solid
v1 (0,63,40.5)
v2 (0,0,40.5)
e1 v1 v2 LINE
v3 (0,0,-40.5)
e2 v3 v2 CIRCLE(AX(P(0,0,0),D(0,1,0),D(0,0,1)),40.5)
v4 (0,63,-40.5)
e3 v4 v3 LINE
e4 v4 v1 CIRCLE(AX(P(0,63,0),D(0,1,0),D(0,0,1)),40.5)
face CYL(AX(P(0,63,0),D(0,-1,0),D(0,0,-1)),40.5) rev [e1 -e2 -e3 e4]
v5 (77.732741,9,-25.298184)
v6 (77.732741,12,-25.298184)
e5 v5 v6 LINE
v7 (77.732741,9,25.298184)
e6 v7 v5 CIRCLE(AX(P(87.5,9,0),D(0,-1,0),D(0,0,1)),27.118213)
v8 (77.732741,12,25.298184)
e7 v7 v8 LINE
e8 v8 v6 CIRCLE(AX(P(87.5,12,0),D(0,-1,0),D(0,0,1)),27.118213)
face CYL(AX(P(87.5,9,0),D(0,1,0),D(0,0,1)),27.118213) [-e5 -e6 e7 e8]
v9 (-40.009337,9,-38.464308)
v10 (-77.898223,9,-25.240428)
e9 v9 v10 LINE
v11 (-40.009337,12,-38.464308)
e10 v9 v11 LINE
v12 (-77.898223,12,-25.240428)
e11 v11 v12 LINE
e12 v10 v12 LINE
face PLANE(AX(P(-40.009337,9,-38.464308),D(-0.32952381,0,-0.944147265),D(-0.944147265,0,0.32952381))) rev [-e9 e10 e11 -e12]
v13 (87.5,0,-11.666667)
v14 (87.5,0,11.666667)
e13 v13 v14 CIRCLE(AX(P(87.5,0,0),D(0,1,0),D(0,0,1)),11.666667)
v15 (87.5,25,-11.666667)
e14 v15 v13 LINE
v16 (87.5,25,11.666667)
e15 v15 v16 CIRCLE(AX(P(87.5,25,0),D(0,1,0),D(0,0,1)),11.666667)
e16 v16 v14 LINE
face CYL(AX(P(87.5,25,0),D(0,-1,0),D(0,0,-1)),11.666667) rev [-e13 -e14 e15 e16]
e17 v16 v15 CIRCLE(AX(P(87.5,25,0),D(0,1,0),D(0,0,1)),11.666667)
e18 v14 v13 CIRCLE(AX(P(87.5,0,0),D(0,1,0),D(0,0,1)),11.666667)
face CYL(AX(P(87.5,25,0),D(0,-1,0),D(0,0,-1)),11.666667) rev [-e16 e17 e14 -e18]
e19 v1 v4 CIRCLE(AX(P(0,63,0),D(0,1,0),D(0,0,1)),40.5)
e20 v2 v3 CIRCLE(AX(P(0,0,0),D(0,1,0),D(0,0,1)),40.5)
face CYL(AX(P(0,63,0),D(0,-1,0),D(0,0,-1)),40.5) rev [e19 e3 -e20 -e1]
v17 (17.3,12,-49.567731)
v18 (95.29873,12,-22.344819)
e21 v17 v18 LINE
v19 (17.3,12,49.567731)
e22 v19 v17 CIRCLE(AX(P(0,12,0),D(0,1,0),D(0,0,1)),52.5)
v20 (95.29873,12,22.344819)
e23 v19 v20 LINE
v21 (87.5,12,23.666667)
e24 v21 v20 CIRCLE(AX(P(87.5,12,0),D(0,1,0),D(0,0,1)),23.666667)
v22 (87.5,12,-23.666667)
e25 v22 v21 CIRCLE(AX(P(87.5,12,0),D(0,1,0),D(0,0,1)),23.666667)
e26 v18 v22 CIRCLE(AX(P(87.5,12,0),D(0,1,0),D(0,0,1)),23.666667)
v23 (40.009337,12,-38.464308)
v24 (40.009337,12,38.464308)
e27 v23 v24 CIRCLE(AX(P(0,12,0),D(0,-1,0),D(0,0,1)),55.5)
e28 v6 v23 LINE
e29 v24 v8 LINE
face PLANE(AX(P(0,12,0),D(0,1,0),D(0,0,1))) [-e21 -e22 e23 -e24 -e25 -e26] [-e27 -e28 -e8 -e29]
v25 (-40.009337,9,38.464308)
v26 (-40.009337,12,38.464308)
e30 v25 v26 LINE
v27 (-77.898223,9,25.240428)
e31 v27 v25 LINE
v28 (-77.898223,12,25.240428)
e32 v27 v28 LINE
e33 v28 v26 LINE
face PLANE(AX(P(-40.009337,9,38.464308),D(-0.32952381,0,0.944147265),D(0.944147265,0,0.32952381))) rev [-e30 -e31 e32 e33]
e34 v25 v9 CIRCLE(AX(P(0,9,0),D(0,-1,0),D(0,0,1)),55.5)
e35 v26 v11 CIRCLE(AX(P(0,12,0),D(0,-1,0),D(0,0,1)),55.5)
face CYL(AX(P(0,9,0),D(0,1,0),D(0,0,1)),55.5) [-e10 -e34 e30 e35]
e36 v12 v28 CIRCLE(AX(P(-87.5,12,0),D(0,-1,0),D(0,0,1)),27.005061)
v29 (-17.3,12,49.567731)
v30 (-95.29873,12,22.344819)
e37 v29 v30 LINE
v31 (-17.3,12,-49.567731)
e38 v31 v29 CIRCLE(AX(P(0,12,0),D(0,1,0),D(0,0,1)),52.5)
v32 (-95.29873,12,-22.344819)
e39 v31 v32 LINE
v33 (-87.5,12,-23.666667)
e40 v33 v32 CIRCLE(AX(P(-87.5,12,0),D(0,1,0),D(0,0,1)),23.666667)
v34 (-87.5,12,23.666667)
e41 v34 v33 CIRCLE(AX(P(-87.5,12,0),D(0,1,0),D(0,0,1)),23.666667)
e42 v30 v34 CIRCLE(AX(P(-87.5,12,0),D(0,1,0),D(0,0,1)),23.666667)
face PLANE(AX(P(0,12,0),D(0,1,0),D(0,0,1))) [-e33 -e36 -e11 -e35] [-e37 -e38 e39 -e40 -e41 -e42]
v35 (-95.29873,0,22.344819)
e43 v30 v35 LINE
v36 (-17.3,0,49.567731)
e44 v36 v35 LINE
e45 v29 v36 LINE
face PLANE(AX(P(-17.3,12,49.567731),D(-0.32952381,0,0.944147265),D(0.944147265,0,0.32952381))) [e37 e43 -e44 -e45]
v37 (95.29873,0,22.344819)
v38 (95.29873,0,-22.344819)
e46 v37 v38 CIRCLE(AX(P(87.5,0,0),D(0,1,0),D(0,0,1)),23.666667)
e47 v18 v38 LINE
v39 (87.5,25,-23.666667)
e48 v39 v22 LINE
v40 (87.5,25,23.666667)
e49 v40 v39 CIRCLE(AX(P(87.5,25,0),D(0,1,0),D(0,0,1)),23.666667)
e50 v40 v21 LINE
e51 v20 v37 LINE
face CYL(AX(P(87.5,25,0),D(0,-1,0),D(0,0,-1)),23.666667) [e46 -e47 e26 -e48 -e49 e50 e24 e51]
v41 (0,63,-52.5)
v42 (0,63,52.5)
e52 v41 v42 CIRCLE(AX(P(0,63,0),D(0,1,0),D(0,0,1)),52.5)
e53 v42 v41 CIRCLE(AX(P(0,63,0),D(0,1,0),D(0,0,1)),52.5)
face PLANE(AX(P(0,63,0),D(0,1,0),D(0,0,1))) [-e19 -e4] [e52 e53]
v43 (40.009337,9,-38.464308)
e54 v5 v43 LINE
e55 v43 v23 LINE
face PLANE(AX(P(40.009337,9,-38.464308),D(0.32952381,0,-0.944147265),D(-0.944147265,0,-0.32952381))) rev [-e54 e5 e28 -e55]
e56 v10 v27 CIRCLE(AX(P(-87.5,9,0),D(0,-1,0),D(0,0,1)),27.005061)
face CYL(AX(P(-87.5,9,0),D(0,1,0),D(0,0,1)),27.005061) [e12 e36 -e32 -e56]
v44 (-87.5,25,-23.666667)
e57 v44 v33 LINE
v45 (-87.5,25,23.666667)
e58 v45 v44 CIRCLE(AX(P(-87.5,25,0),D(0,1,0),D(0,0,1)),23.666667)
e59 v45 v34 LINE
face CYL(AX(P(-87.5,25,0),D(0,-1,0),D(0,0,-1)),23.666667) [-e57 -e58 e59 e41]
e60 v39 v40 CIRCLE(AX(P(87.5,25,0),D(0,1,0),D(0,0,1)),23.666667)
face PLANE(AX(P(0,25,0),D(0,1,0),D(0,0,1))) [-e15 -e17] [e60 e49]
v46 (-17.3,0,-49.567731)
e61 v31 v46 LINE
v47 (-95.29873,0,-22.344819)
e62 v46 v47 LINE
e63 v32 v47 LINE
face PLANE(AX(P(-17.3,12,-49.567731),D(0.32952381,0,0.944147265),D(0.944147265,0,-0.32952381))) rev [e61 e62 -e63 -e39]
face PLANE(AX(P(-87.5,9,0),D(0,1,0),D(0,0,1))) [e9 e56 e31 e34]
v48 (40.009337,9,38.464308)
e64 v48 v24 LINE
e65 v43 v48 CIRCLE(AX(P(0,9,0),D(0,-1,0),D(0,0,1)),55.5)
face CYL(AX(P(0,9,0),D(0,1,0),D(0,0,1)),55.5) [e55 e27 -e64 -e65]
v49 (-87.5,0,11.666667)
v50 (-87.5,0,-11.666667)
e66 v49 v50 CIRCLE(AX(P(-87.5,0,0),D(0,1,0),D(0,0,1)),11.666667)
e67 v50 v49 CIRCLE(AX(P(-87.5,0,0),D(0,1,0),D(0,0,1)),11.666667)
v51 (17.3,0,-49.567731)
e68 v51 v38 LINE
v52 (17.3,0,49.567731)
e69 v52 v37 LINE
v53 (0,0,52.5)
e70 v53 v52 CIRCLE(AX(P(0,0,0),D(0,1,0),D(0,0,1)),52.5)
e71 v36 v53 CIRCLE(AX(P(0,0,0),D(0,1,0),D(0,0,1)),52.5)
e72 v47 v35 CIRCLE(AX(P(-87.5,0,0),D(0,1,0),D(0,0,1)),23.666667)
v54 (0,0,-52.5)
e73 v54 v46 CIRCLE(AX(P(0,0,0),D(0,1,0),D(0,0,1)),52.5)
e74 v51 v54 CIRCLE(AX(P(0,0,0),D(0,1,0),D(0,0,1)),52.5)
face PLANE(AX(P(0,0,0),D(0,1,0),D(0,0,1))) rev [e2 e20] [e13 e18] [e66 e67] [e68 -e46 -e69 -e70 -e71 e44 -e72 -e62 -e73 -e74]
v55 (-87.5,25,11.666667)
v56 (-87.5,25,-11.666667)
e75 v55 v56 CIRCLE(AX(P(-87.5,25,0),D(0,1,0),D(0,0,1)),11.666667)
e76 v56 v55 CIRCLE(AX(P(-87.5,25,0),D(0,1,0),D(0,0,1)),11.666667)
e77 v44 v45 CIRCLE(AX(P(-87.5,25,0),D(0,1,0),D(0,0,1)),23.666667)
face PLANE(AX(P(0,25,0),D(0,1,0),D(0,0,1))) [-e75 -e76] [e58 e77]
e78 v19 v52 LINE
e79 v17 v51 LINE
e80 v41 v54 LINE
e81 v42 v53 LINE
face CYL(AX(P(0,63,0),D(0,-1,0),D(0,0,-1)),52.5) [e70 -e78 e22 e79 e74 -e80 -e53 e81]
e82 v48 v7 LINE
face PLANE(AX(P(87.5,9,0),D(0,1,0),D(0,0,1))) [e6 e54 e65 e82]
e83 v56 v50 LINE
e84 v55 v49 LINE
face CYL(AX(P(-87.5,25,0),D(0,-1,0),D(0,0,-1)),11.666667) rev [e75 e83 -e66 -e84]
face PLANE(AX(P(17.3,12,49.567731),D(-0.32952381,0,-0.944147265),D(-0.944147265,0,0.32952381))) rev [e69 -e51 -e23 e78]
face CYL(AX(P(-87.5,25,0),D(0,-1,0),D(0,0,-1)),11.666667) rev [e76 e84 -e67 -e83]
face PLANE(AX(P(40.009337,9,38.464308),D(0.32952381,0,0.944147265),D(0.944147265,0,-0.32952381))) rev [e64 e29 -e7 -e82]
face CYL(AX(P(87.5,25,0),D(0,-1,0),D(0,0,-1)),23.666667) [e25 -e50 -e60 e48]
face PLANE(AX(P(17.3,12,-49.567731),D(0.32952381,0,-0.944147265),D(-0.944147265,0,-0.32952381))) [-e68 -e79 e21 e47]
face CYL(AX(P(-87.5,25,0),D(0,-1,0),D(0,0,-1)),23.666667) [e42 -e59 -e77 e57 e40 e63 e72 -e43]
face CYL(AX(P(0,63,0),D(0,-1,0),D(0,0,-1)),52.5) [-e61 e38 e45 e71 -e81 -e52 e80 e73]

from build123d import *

# Parameters (mm, degrees)
HOUSING_PROFILE_SKETCH_R      = 52.5
HOUSING_PROFILE_SKETCH_R_2    = 40.5
BEARING_HOUSING_BOSS_DEPTH    = 63
MOUNTING_FLANGE_12MM_DEPTH    = 12
SKETCH1_4_R                   = 23.666666665
SKETCH1_4_R_2                 = 11.666666665
BOLT_LUG_BOSSES_25MM_DEPTH    = 25
FLANGE_POCKETS_3MM_DEEP_DEPTH = 3


with BuildPart() as part:
    # Housing Profile Sketch → Bearing Housing Boss (new body)
    with BuildSketch(Plane(origin=(0, 0, 0), x_dir=(1, 0, 0), z_dir=(0, 1, 0))):
        with Locations(Location((0, 0, 0), (0, 0, 270))):
            Circle(HOUSING_PROFILE_SKETCH_R)
        with Locations(Location((0, 0, 0), (0, 0, 270))):
            Circle(HOUSING_PROFILE_SKETCH_R_2, mode=Mode.SUBTRACT)
    extrude(amount=BEARING_HOUSING_BOSS_DEPTH)

    # Sketch1_3 → Mounting Flange 12mm (add)
    with BuildSketch(Plane(origin=(0, 0, 0), x_dir=(1, 0, 0), z_dir=(0, 1, 0))):
        with BuildLine():
            ThreePointArc((-17.300000001, -49.567731439), (-52.5, 0), (-17.300000001, 49.567731439))
            Line((-17.300000001, 49.567731439), (-95.298730159, 22.344818615))
            ThreePointArc((-95.298730159, 22.344818615), (-73.797059367, 19.296127307), (-63.833333335, 0))
            ThreePointArc((-63.833333335, 0), (-73.797059367, -19.296127307), (-95.298730159, -22.344818615))
            Line((-95.298730159, -22.344818615), (-17.300000001, -49.567731439))
        make_face()
        with BuildLine():
            Line((95.298730159, 22.344818615), (17.300000001, 49.567731439))
            ThreePointArc((17.300000001, 49.567731439), (42.804789452, 30.397368307), (52.5, 0))
            ThreePointArc((52.5, 0), (42.804789452, -30.397368307), (17.300000001, -49.567731439))
            Line((17.300000001, -49.567731439), (95.298730159, -22.344818615))
            ThreePointArc((95.298730159, -22.344818615), (63.833333335, 0), (95.298730159, 22.344818615))
        make_face()
    extrude(amount=MOUNTING_FLANGE_12MM_DEPTH)

    # Sketch1_4 → Bolt Lug Bosses 25mm (add)
    # profile 1 of 2: a face of its own
    with BuildSketch(Plane(origin=(0, 0, 0), x_dir=(1, 0, 0), z_dir=(0, 1, 0))):
        with Locations(Location((-87.5, 0, 0), (0, 0, 109.239875226))):
            Circle(SKETCH1_4_R)
        with Locations(Location((-87.5, 0, 0), (0, 0, 270))):
            Circle(SKETCH1_4_R_2, mode=Mode.SUBTRACT)
    # profile 2 of 2: a face of its own
    with BuildSketch(Plane(origin=(0, 0, 0), x_dir=(1, 0, 0), z_dir=(0, 1, 0))):
        with Locations(Location((87.5, 0, 0), (0, 0, 70.760124774))):
            Circle(SKETCH1_4_R)
        with Locations(Location((87.5, 0, 0), (0, 0, 270))):
            Circle(SKETCH1_4_R_2, mode=Mode.SUBTRACT)
    extrude(amount=BOLT_LUG_BOSSES_25MM_DEPTH)

    # Flange Pocket Sketch → Flange Pockets 3mm Deep (cut)
    with BuildSketch(Plane(origin=(0, 12, 0), x_dir=(1, 0, 0), z_dir=(0, 1, 0))):
        with BuildLine():
            Line((-40.009336858, 38.464307665), (-77.89822284, 25.240427764))
            ThreePointArc((-77.89822284, 25.240427764), (-60.494939024, 0), (-77.89822284, -25.240427764))
            Line((-77.89822284, -25.240427764), (-40.009336858, -38.464307665))
            ThreePointArc((-40.009336858, -38.464307665), (-55.5, 0), (-40.009336858, 38.464307665))
        make_face()
        with BuildLine():
            Line((40.009336858, 38.464307665), (77.732740957, 25.298183818))
            ThreePointArc((77.732740957, 25.298183818), (60.381787417, 0), (77.732740957, -25.298183818))
            Line((77.732740957, -25.298183818), (40.009336858, -38.464307665))
            ThreePointArc((40.009336858, -38.464307665), (55.5, 0), (40.009336858, 38.464307665))
        make_face()
    extrude(amount=-FLANGE_POCKETS_3MM_DEEP_DEPTH, mode=Mode.SUBTRACT)


solid = part.part
